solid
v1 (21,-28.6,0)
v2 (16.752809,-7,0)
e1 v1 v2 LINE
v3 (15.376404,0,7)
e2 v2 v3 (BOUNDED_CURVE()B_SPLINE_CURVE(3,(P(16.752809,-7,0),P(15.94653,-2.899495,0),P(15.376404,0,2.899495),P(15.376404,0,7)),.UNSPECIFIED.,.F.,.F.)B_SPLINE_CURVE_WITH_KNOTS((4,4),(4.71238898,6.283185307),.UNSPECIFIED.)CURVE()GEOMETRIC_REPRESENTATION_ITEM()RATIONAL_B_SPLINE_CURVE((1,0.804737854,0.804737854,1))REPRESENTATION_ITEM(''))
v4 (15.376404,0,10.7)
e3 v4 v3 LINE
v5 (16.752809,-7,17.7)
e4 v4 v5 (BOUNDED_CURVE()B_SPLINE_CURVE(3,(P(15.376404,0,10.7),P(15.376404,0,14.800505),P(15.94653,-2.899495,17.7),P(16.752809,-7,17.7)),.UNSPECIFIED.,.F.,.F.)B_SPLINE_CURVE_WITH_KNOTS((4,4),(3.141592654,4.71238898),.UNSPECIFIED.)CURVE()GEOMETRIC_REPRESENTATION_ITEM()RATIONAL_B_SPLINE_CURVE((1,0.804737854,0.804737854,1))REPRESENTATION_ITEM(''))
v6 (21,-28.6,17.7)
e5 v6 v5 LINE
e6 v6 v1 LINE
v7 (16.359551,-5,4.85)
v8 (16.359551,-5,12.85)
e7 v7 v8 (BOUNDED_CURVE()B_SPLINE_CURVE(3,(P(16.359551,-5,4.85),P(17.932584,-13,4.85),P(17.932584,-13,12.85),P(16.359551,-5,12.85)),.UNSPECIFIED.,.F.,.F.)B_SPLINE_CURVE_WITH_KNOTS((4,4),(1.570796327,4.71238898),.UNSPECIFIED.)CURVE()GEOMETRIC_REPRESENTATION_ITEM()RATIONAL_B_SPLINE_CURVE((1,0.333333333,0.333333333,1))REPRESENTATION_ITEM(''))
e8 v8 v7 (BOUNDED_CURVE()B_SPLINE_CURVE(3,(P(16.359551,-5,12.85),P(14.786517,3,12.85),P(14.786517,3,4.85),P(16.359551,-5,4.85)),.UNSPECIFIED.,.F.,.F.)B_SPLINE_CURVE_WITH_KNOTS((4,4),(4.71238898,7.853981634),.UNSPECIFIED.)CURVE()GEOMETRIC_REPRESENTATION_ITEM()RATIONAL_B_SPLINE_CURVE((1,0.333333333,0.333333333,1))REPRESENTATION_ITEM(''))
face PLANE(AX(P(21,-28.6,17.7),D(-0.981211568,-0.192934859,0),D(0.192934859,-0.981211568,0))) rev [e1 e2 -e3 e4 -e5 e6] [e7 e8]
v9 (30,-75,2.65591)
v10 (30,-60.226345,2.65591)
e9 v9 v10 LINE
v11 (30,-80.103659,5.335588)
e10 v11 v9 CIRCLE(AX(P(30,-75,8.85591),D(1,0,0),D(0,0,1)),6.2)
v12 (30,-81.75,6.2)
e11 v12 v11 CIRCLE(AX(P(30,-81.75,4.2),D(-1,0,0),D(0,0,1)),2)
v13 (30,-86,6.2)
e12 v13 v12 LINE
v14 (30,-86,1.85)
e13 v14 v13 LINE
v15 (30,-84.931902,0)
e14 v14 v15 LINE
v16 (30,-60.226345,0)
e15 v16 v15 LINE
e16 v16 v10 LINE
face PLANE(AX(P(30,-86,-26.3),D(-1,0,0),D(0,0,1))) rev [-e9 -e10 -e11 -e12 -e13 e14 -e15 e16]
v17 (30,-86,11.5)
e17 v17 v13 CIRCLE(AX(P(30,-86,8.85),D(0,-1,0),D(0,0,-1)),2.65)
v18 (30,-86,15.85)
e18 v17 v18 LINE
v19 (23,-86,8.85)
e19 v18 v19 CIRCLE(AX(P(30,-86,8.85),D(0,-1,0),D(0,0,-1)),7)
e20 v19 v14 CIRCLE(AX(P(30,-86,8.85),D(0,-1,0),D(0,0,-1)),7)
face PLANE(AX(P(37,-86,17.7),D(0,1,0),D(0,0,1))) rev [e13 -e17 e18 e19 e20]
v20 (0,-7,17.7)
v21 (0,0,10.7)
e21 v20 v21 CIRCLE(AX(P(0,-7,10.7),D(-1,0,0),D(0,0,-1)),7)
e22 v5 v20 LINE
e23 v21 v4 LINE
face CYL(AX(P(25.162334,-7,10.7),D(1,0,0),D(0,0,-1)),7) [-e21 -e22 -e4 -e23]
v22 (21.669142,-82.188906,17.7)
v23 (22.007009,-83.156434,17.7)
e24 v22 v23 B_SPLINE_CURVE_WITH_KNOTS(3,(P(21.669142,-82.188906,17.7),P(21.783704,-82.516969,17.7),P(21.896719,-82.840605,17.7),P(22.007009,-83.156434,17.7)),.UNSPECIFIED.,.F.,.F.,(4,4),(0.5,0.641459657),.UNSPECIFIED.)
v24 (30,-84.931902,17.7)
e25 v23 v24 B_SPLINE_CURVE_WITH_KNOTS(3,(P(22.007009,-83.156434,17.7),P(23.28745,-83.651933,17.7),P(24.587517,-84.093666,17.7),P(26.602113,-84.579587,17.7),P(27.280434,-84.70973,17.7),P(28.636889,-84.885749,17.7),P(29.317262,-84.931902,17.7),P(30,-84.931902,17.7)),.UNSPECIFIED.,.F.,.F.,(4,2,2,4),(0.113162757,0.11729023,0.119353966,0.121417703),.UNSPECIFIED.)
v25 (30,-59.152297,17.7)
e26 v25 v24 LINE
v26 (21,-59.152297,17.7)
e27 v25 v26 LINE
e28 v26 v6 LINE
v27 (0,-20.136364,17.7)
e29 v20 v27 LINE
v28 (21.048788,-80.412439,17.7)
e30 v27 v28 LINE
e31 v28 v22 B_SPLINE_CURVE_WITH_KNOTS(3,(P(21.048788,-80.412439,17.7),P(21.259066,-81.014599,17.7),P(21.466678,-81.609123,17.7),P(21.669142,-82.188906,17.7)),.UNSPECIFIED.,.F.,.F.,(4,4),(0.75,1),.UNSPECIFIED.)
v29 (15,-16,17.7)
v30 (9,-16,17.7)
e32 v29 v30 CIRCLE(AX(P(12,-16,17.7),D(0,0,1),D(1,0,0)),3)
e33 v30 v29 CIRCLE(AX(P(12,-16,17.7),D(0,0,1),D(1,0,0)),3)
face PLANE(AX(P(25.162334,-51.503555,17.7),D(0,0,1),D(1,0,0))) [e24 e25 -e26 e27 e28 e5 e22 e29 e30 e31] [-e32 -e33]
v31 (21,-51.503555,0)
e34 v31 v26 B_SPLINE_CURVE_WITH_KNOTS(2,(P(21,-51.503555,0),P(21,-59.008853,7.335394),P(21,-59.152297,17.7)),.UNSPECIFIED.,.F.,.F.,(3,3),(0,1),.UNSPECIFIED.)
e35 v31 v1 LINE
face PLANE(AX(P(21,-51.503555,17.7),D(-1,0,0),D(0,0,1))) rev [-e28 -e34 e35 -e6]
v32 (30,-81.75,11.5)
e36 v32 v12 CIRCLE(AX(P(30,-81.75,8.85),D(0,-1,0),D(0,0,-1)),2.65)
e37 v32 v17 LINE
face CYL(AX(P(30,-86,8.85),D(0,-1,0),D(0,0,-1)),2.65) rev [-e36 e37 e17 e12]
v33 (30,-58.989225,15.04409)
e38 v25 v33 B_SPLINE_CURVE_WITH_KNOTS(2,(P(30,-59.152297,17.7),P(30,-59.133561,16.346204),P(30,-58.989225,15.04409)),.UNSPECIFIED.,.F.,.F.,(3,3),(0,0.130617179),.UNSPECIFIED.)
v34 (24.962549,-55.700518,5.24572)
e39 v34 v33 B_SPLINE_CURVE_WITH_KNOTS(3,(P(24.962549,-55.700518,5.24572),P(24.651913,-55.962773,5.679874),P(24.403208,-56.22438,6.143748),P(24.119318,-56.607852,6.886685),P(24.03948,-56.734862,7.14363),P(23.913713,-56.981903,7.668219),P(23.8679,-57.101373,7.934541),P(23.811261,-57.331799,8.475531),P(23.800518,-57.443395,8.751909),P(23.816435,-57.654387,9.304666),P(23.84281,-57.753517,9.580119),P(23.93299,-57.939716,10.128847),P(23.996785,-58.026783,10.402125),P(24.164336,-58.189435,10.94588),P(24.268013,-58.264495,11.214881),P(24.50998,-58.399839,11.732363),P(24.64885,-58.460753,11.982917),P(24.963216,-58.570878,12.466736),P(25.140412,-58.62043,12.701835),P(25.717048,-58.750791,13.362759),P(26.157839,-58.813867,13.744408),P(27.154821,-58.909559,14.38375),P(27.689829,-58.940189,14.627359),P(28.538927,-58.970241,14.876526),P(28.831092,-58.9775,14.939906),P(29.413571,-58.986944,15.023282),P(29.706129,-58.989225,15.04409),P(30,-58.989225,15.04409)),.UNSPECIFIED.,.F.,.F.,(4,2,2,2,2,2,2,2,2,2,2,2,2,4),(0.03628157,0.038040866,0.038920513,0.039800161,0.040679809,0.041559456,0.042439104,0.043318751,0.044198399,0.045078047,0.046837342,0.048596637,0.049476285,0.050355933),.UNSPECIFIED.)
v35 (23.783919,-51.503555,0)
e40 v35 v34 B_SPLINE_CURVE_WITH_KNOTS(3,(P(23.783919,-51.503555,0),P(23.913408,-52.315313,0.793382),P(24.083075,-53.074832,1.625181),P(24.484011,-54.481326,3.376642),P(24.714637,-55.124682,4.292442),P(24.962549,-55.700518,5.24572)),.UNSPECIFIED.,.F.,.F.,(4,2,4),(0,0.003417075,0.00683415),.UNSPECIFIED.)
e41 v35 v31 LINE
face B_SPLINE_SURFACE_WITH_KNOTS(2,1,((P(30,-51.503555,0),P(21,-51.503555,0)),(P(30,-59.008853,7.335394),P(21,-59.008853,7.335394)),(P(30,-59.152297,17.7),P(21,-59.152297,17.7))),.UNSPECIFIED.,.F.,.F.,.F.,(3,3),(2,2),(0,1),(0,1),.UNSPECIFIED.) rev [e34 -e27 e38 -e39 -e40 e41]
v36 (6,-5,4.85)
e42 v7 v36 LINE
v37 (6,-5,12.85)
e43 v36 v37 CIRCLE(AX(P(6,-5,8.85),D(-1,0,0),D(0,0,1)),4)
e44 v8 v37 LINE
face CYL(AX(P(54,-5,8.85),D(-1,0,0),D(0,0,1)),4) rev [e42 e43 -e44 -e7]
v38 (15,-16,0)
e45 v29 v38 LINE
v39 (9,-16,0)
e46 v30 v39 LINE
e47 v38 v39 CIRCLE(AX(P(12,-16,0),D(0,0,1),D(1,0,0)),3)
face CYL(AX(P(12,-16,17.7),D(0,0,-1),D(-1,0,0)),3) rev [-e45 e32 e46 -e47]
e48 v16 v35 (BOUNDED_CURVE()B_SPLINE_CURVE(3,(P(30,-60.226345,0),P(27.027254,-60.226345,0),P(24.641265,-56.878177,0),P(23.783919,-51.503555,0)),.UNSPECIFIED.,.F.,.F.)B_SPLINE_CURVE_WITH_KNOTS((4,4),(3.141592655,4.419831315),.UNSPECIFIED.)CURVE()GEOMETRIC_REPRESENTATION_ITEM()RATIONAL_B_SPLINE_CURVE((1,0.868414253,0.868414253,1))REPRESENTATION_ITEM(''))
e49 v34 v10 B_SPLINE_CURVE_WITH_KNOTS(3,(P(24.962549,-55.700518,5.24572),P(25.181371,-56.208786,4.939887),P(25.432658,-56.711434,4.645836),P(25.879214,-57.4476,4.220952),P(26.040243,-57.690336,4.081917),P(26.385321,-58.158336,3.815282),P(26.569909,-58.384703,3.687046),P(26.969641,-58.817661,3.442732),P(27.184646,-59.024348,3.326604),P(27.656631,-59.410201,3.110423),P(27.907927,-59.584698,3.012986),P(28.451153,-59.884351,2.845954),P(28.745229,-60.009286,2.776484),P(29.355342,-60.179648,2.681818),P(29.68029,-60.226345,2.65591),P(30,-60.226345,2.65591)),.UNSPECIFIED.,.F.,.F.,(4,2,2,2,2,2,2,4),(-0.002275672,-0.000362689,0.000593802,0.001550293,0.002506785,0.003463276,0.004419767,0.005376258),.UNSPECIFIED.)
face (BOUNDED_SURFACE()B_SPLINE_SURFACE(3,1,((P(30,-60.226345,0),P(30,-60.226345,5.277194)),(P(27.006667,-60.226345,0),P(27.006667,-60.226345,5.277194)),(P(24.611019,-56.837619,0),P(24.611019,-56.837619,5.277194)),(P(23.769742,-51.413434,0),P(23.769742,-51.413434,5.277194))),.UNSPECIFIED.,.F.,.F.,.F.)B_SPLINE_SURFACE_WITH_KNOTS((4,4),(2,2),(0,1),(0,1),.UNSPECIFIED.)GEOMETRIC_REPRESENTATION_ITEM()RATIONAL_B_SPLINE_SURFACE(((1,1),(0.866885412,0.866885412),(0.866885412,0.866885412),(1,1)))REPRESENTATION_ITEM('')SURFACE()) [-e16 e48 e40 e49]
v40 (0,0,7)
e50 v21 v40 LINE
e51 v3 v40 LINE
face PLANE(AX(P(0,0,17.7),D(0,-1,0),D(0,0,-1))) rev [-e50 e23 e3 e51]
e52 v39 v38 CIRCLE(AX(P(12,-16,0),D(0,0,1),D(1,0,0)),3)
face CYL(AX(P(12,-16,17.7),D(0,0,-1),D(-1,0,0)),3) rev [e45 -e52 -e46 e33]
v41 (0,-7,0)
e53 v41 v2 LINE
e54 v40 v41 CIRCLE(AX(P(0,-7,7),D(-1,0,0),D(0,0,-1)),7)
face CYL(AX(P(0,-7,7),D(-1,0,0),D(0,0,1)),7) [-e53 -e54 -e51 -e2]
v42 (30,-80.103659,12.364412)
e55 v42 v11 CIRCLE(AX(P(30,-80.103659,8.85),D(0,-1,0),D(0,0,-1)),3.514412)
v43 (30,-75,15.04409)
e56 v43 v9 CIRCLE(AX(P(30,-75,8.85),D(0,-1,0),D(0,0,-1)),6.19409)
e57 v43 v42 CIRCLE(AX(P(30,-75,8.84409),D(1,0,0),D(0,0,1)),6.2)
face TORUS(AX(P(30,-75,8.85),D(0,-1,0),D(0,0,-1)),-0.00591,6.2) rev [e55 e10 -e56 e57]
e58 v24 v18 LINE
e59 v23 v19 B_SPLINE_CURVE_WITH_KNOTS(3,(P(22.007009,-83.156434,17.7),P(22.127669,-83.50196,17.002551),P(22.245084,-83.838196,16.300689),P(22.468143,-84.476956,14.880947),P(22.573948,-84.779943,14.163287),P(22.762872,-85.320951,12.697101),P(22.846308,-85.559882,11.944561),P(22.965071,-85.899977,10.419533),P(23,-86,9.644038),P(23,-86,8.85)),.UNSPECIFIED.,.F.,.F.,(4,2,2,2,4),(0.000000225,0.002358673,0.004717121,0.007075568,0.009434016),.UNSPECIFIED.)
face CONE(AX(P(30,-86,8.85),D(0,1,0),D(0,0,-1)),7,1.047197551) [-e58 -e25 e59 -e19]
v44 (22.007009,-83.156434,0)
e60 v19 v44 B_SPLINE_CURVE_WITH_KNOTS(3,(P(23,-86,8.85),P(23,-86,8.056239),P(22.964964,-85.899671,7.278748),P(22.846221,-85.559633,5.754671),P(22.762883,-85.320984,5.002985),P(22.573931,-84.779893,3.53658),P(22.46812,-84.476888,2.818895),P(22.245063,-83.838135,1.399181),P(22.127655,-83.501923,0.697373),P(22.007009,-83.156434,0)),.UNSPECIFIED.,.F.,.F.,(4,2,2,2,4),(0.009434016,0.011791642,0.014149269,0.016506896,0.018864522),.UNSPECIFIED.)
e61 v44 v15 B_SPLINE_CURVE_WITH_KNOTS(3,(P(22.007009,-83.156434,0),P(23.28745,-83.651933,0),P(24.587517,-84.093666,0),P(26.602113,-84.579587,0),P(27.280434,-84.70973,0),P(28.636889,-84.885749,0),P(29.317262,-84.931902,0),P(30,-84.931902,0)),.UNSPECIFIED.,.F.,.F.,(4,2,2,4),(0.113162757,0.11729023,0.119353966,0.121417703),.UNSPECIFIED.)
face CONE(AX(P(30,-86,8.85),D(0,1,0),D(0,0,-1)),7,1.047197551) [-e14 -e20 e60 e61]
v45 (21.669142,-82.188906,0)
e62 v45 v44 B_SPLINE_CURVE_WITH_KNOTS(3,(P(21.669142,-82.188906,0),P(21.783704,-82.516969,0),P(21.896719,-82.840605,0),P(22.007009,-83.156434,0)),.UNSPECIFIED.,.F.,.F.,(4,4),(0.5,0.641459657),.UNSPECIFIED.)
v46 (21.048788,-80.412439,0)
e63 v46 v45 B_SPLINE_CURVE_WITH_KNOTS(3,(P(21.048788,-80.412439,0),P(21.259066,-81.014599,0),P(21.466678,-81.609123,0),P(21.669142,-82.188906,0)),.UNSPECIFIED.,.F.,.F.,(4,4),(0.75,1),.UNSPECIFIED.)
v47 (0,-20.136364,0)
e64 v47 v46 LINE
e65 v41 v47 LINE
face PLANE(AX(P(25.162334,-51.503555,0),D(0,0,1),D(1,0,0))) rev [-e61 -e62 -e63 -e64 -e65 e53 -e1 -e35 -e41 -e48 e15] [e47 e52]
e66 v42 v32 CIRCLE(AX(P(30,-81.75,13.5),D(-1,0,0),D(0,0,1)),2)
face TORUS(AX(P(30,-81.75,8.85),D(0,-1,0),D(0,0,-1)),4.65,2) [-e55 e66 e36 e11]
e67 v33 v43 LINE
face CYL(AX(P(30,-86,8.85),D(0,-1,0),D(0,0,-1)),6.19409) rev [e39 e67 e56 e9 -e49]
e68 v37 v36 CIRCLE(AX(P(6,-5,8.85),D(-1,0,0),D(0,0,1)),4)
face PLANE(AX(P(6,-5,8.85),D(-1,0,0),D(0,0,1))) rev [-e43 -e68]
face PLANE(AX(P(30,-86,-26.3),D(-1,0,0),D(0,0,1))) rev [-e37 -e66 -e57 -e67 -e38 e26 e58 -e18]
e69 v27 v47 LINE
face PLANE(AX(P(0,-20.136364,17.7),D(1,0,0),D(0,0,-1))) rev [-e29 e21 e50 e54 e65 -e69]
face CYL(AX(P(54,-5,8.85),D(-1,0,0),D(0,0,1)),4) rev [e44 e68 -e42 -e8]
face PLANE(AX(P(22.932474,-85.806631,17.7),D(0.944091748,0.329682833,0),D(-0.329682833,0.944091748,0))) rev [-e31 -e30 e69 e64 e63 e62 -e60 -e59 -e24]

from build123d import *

# Parameters (mm, degrees)
SKETCH1_R                      = 3
BOSS_EXTRUDE2_DEPTH            = 17.7
CUT_EXTRUDE1_REACH             = 94.786
CUT_EXTRUDE1_DIRECTION_2_REACH = 94.786
SKETCH6_RX                     = 12.258033
SKETCH6_RY                     = 6.491927
CUT_EXTRUDE2_DEPTH             = 48.7
SKETCH7_R                      = 6.19409
CUT_EXTRUDE3_DEPTH             = 60.7
SKETCH8_R                      = 4
CUT_EXTRUDE4_DEPTH             = 48
FILLET1_R                      = 7
SKETCH10_OUTSIDE_W             = 249.546
SKETCH10_OUTSIDE_H             = 207.246
SKETCH10_OUTSIDE_R             = 7
CUT_EXTRUDE5_DEPTH             = 48
CUT_EXTRUDE5_TAPER             = 60
CUT_EXTRUDE7_DEPTH             = 44


with BuildPart() as part:
    # Sketch1 → Boss-Extrude2 (new body)
    with BuildSketch(Plane.XY):
        with BuildLine():
            Line((39, -51.503555), (34.837666, -51.503555))
            Line((34.837666, -51.503555), (25.162334, -51.503555))
            Line((25.162334, -51.503555), (21, -51.503555))
            Line((21, -51.503555), (21, -28.6))
            Line((21, -28.6), (15.376404, 0))
            Line((15.376404, 0), (0, 0))
            Line((0, 0), (0, -20.136364))
            Line((0, -20.136364), (21.048788, -80.412439))
            add(Edge.make_bspline(
                [(21.669142, -82.188906), (21.466678, -81.609123), (21.259066, -81.014599), (21.048788, -80.412439)],
                knots=[0.75, 0.75, 0.75, 0.75, 1, 1, 1, 1], degree=3))
            add(Edge.make_bspline(
                [(22.255532, -83.868113), (22.06924, -83.334643), (21.871606, -82.768689), (21.669142, -82.188906)],
                knots=[0.5, 0.5, 0.5, 0.5, 0.75, 0.75, 0.75, 0.75], degree=3))
            add(Edge.make_bspline(
                [(22.524034, -84.637007), (22.439154, -84.393941), (22.348677, -84.134848), (22.255532, -83.868113)],
                knots=[0.375, 0.375, 0.375, 0.375, 0.5, 0.5, 0.5, 0.5], degree=3))
            add(Edge.make_bspline(
                [(22.758263, -85.307753), (22.688292, -85.107381), (22.608914, -84.880073), (22.524034, -84.637007)],
                knots=[0.25, 0.25, 0.25, 0.25, 0.375, 0.375, 0.375, 0.375], degree=3))
            add(Edge.make_bspline(
                [(22.855261, -85.585519), (22.825847, -85.50129), (22.793248, -85.407938), (22.758263, -85.307753)],
                knots=[0.1875, 0.1875, 0.1875, 0.1875, 0.25, 0.25, 0.25, 0.25], degree=3))
            add(Edge.make_bspline(
                [(22.932474, -85.806631), (22.910958, -85.745015), (22.884674, -85.669748), (22.855261, -85.585519)],
                knots=[0.125, 0.125, 0.125, 0.125, 0.1875, 0.1875, 0.1875, 0.1875], degree=3))
            add(Edge.make_bspline(
                [(23, -86), (22.975508, -85.929864), (22.932474, -85.806631)],
                knots=[0, 0, 0, 0.125, 0.125, 0.125], degree=2))
            Line((23, -86), (37, -86))
            add(Edge.make_bspline(
                [(37.068167, -85.804796), (37.025162, -85.927946), (37, -86)],
                knots=[0.875, 0.875, 0.875, 1, 1, 1], degree=2))
            add(Edge.make_bspline(
                [(37.242328, -85.306061), (37.171936, -85.507639), (37.111171, -85.681646), (37.068167, -85.804796)],
                knots=[0.75, 0.75, 0.75, 0.75, 0.875, 0.875, 0.875, 0.875], degree=3))
            add(Edge.make_bspline(
                [(37.47673, -84.63482), (37.392157, -84.877005), (37.31272, -85.104482), (37.242328, -85.306061)],
                knots=[0.625, 0.625, 0.625, 0.625, 0.75, 0.75, 0.75, 0.75], degree=3))
            add(Edge.make_bspline(
                [(37.744144, -83.869041), (37.651111, -84.135454), (37.561302, -84.392634), (37.47673, -84.63482)],
                knots=[0.5, 0.5, 0.5, 0.5, 0.625, 0.625, 0.625, 0.625], degree=3))
            add(Edge.make_bspline(
                [(38.330881, -82.18884), (38.128355, -82.768803), (37.930211, -83.336215), (37.744144, -83.869041)],
                knots=[0.25, 0.25, 0.25, 0.25, 0.5, 0.5, 0.5, 0.5], degree=3))
            add(Edge.make_bspline(
                [(38.951212, -80.412439), (38.741, -81.014409), (38.533408, -81.608878), (38.330881, -82.18884)],
                knots=[0, 0, 0, 0, 0.25, 0.25, 0.25, 0.25], degree=3))
            Line((38.951212, -80.412439), (60, -20.136364))
            Line((60, -20.136364), (60, 0))
            Line((60, 0), (44.6, 0))
            Line((44.6, 0), (39, -28))
            Line((39, -28), (39, -51.503555))
        make_face()
        with Locations((48, -16)):
            Circle(SKETCH1_R, mode=Mode.SUBTRACT)
        with Locations((12, -16)):
            Circle(SKETCH1_R, mode=Mode.SUBTRACT)
    extrude(amount=BOSS_EXTRUDE2_DEPTH)

    # Sketch2 → Cut-Revolve2 (revolve, cut)
    with BuildSketch(Plane.ZY.offset(-30), mode=Mode.PRIVATE) as cut_revolve2_sk:
        with BuildLine():
            ThreePointArc((11.5, -81.75), (11.729241, -80.820262), (12.364412, -80.103659))
            ThreePointArc((12.364412, -80.103659), (14.333443, -77.882187), (15.04409, -75))
            Line((15.04409, -75), (15.04409, -57.48))
            Line((15.04409, -57.48), (8.85, -57.48))
            Line((8.85, -57.48), (8.85, -86))
            Line((8.85, -86), (11.5, -86))
            Line((11.5, -86), (11.5, -81.75))
        make_face()
    revolve(cut_revolve2_sk.sketch.rotate(Axis((30, -86, 8.85), (0, 1, 0)), 180), axis=Axis((30, -86, 8.85), (0, 1, 0)), mode=Mode.SUBTRACT)

    # Cut-Extrude1: up to this face of the body (flat: up to its plane)
    cut_extrude1_end = Plane(part.part.faces().sort_by_distance((39, -39.751777, 8.85))[0])
    # Sketch3 → Cut-Extrude1 (cut, up to the picked face)
    with BuildSketch(Plane.ZY.offset(-30), mode=Mode.PRIVATE) as cut_extrude1_sk1:
        with BuildLine():
            Line((0, -51.503555), (17.7, -51.503555))
            Line((17.7, -51.503555), (17.7, -59.152297))
            add(Edge.make_bspline(
                [(17.7, -59.152297), (7.335394, -59.008853), (0, -51.503555)],
                knots=[0, 0, 0, 1, 1, 1], degree=2))
        make_face()
    cut_extrude1_tool1 = split(extrude(cut_extrude1_sk1.sketch, amount=-CUT_EXTRUDE1_REACH, mode=Mode.PRIVATE), bisect_by=cut_extrude1_end, keep=Keep.BOTH, mode=Mode.PRIVATE)
    add(cut_extrude1_tool1.solids().sort_by(Axis((30, -54.604638, 10.907898), (1, 0, 0)))[0], mode=Mode.SUBTRACT)

    # Cut-Extrude1 direction 2: up to this face of the body (flat: up to its plane)
    cut_extrude1_direction_2_end = Plane(part.part.faces().sort_by_distance((21, -40.051777, 8.85))[0])
    # Sketch3 → Cut-Extrude1 direction 2 (cut, up to the picked face)
    with BuildSketch(Plane.ZY.offset(-30), mode=Mode.PRIVATE) as cut_extrude1_direction_2_sk1:
        with BuildLine():
            Line((0, -51.503555), (17.7, -51.503555))
            Line((17.7, -51.503555), (17.7, -59.152297))
            add(Edge.make_bspline(
                [(17.7, -59.152297), (7.335394, -59.008853), (0, -51.503555)],
                knots=[0, 0, 0, 1, 1, 1], degree=2))
        make_face()
    cut_extrude1_direction_2_tool1 = split(extrude(cut_extrude1_direction_2_sk1.sketch, amount=CUT_EXTRUDE1_DIRECTION_2_REACH, mode=Mode.PRIVATE), bisect_by=cut_extrude1_direction_2_end, keep=Keep.BOTH, mode=Mode.PRIVATE)
    add(cut_extrude1_direction_2_tool1.solids().sort_by(Axis((30, -54.604638, 10.907898), (-1, 0, 0)))[0], mode=Mode.SUBTRACT)

    # Sketch6 → Cut-Extrude2 (cut)
    with BuildSketch(Plane(origin=(0, 0, 8.85), x_dir=(-1, 0, 0), z_dir=(0, 0, -1))):
        with Locations(Location((-30, -47.968312), (0, 0, 90))):
            Ellipse(SKETCH6_RX, SKETCH6_RY)
    extrude(amount=CUT_EXTRUDE2_DEPTH, mode=Mode.SUBTRACT)

    # Sketch7 → Cut-Extrude3 (cut)
    with BuildSketch(Plane(origin=(0, 0, 0), x_dir=(1, 0, 0), z_dir=(0, 1, 0))):
        with Locations(Location((30, -8.85, 0), (0, 0, 90))):
            Circle(SKETCH7_R)
    extrude(amount=-CUT_EXTRUDE3_DEPTH, mode=Mode.SUBTRACT)

    # Sketch8 → Cut-Extrude4 (cut)
    with BuildSketch(Plane.ZY.offset(-6)):
        with Locations((8.85, -5)):
            Circle(SKETCH8_R)
    extrude(amount=-CUT_EXTRUDE4_DEPTH, mode=Mode.SUBTRACT)

    # Fillet1
    fillet1_edges = [part.edges().sort_by_distance(p)[0] for p in [
        (7.688202, 0, 17.7),
        (52.3, 0, 0),
        (7.688202, 0, 0),
        (52.3, 0, 17.7),
    ]]
    fillet(fillet1_edges, radius=FILLET1_R)

    # Sketch10 outside → Cut-Extrude5 (cut)
    with BuildSketch(Plane.XZ.offset(86)):
        with Locations((30, 8.85)):
            Rectangle(SKETCH10_OUTSIDE_W, SKETCH10_OUTSIDE_H)
        with Locations((30, 8.85)):
            Circle(SKETCH10_OUTSIDE_R, mode=Mode.SUBTRACT)
    extrude(amount=-CUT_EXTRUDE5_DEPTH, taper=CUT_EXTRUDE5_TAPER, mode=Mode.SUBTRACT)

    # Sketch12 → Cut-Extrude7 (cut)
    with BuildSketch(Plane.XY.offset(17.7)):
        Polygon((30, -86), (30, 13.730719), (80.816645, 10.061019), (70.681282, -110.340096), align=None)
    extrude(amount=-CUT_EXTRUDE7_DEPTH, mode=Mode.SUBTRACT)


solid = part.part
